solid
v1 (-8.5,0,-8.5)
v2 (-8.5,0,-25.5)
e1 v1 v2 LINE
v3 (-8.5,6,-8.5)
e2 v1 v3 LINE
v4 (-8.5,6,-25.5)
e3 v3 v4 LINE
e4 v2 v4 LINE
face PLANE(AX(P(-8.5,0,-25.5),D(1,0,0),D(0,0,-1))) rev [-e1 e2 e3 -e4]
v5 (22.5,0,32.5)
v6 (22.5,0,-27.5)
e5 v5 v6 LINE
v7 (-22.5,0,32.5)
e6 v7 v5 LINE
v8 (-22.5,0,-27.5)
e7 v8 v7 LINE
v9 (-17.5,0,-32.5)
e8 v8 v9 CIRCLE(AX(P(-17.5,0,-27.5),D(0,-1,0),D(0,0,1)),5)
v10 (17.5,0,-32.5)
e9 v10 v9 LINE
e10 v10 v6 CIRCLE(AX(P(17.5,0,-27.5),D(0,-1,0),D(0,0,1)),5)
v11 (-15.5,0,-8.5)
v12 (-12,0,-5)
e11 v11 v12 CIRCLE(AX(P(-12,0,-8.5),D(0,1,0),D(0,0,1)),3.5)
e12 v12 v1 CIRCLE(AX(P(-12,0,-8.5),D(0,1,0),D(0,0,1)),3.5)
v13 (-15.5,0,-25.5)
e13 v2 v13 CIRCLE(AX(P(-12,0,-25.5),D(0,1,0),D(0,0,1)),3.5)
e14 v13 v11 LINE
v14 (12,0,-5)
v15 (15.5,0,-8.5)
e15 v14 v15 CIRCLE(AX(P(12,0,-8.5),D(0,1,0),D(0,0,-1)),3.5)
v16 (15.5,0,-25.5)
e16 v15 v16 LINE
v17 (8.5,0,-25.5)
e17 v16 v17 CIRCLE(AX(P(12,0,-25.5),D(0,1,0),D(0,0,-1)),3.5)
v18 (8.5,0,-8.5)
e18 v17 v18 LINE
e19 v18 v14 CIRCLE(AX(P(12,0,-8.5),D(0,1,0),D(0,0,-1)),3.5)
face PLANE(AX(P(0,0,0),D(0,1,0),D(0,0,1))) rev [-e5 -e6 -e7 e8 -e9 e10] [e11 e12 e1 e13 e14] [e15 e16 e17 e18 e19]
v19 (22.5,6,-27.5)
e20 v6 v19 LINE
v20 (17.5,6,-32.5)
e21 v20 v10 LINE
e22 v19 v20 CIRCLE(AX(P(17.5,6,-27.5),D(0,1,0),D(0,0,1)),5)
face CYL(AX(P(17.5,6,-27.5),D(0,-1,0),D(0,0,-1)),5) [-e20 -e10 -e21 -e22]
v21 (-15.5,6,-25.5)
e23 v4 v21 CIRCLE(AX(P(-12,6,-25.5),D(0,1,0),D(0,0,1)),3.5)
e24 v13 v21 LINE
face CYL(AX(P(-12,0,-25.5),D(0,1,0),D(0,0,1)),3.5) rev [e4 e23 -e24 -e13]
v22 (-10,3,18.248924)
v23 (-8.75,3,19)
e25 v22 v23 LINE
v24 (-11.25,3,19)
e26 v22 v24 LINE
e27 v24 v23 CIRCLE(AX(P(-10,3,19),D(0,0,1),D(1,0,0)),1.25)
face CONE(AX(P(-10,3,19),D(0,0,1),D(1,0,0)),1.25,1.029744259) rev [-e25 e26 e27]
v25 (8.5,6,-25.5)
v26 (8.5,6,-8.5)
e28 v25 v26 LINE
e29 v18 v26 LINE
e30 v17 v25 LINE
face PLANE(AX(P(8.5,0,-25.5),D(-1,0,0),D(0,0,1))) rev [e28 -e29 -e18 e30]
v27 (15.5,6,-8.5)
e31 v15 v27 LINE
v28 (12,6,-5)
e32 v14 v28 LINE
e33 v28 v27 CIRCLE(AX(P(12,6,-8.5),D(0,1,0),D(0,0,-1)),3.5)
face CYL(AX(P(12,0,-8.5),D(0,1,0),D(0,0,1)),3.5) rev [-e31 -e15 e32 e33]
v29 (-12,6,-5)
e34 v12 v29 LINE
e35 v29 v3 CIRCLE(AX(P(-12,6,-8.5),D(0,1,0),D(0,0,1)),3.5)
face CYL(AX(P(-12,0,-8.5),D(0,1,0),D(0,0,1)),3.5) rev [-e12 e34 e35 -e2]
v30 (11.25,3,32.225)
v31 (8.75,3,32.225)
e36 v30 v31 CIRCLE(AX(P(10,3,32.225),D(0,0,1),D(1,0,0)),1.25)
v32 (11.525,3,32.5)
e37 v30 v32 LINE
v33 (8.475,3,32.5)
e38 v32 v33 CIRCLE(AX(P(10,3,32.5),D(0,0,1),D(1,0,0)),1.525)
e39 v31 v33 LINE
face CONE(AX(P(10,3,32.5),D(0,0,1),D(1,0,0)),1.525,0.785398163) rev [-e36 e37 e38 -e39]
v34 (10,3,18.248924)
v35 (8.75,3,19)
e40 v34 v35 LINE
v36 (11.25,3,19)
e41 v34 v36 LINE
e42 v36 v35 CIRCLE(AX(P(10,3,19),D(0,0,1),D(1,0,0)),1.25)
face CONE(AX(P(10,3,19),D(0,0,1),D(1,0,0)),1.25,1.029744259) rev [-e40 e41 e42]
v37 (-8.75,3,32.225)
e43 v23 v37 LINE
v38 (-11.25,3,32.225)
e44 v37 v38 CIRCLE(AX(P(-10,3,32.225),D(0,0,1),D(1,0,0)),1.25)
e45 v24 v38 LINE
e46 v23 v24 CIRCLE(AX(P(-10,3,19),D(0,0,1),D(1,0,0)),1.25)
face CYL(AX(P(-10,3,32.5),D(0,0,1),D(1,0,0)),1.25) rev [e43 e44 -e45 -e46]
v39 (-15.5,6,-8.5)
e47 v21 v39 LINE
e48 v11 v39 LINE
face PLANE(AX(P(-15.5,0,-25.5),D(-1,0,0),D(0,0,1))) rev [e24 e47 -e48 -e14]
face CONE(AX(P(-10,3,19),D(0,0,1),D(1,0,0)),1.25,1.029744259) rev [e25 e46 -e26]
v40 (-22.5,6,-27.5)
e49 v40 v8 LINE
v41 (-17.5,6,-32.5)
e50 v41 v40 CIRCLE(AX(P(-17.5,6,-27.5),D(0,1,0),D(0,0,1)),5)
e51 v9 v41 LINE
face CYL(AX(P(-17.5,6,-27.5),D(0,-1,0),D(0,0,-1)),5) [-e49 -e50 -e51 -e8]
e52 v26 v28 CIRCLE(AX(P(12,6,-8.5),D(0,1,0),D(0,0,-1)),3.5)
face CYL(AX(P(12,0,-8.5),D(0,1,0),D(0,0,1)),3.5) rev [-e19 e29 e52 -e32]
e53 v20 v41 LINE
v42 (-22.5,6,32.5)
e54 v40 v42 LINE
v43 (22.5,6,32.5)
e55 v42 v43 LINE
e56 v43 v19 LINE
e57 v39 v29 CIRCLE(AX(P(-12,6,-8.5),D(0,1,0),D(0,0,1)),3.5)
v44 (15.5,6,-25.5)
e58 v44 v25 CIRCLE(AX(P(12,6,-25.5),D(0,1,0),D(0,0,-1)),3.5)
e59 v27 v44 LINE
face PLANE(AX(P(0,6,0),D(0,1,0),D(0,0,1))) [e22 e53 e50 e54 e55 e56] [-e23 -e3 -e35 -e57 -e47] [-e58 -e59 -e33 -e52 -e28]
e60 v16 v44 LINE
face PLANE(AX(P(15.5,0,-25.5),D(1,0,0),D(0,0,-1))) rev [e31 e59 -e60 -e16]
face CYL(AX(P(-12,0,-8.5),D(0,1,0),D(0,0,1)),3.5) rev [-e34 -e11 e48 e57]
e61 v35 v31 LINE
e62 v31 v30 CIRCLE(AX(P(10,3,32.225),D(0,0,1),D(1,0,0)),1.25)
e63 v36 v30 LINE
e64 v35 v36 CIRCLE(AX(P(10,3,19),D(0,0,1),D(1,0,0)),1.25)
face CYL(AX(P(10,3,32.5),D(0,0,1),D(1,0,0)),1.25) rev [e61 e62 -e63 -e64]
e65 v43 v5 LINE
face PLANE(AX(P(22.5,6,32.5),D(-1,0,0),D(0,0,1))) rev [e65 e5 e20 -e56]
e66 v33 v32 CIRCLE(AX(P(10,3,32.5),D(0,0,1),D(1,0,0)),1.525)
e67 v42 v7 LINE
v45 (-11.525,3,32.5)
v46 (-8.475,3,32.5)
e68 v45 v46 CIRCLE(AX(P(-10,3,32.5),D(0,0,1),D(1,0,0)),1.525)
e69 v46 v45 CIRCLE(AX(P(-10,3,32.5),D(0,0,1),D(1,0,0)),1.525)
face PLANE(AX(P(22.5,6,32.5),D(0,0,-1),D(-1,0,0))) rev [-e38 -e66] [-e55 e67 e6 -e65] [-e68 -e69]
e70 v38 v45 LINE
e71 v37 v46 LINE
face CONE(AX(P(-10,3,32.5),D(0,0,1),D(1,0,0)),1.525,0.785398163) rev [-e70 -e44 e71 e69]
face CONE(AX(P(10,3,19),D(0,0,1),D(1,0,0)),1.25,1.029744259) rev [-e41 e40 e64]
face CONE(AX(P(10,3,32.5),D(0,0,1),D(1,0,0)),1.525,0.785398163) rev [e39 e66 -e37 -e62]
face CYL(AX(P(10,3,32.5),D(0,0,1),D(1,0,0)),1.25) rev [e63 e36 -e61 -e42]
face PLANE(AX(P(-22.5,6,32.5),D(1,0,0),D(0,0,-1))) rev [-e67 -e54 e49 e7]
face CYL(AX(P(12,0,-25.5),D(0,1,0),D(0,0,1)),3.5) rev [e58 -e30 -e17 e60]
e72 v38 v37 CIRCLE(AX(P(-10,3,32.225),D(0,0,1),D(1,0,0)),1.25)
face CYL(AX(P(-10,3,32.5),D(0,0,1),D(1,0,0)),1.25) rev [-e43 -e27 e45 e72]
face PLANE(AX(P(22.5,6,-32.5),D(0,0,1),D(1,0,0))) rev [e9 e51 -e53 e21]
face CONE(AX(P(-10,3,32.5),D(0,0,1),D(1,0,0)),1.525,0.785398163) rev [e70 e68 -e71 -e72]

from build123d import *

# Parameters (mm, degrees)
SKETCH1_W                   = 45
SKETCH1_H                   = 65
BOSS_EXTRUDE1_DEPTH         = 6
CUT_EXTRUDE1_DEPTH          = 6
FILLET2_R                   = 5
M3_TAPPED_HOLE1_D           = 2.5
M3_TAPPED_HOLE1_DEPTH       = 13.5
M3_TAPPED_HOLE1_CSINK_D     = 3.05
M3_TAPPED_HOLE1_CSINK_ANGLE = 90
M3_TAPPED_HOLE1_TIP         = 0.751075774


with BuildPart() as part:
    # Sketch1 → Boss-Extrude1 (new body)
    with BuildSketch(Plane(origin=(0, 0, 0), x_dir=(1, 0, 0), z_dir=(0, 1, 0))):
        Rectangle(SKETCH1_W, SKETCH1_H)
    extrude(amount=BOSS_EXTRUDE1_DEPTH)

    # Sketch6 → Cut-Extrude1 (cut)
    with BuildSketch(Plane(origin=(0, 6, 0), x_dir=(1, 0, 0), z_dir=(0, 1, 0))):
        with BuildLine():
            Line((-8.5, 25.5), (-8.5, 8.5))
            ThreePointArc((-8.5, 8.5), (-12, 5), (-15.5, 8.5))
            Line((-15.5, 8.5), (-15.5, 25.5))
            ThreePointArc((-15.5, 25.5), (-12, 29), (-8.5, 25.5))
        make_face()
        with BuildLine():
            Line((8.5, 25.5), (8.5, 8.5))
            ThreePointArc((8.5, 8.5), (12, 5), (15.5, 8.5))
            Line((15.5, 8.5), (15.5, 25.5))
            ThreePointArc((15.5, 25.5), (12, 29), (8.5, 25.5))
        make_face()
    extrude(amount=-CUT_EXTRUDE1_DEPTH, mode=Mode.SUBTRACT)

    # Fillet2
    fillet2_edges = [part.edges().sort_by_distance(p)[0] for p in [
        (-22.5, 3, -32.5),
        (22.5, 3, -32.5),
    ]]
    fillet(fillet2_edges, radius=FILLET2_R)

    # M3 Tapped Hole1
    with Locations(Plane.XY.offset(32.5)):
        with Locations((-10, 3), (10, 3)):
            CounterSinkHole(M3_TAPPED_HOLE1_D / 2, M3_TAPPED_HOLE1_CSINK_D / 2, depth=M3_TAPPED_HOLE1_DEPTH, counter_sink_angle=M3_TAPPED_HOLE1_CSINK_ANGLE)
            with Locations((0, 0, -(M3_TAPPED_HOLE1_DEPTH + M3_TAPPED_HOLE1_TIP / 2))):  # 118° drill point
                Cone(0, M3_TAPPED_HOLE1_D / 2, M3_TAPPED_HOLE1_TIP, mode=Mode.SUBTRACT)


solid = part.part
